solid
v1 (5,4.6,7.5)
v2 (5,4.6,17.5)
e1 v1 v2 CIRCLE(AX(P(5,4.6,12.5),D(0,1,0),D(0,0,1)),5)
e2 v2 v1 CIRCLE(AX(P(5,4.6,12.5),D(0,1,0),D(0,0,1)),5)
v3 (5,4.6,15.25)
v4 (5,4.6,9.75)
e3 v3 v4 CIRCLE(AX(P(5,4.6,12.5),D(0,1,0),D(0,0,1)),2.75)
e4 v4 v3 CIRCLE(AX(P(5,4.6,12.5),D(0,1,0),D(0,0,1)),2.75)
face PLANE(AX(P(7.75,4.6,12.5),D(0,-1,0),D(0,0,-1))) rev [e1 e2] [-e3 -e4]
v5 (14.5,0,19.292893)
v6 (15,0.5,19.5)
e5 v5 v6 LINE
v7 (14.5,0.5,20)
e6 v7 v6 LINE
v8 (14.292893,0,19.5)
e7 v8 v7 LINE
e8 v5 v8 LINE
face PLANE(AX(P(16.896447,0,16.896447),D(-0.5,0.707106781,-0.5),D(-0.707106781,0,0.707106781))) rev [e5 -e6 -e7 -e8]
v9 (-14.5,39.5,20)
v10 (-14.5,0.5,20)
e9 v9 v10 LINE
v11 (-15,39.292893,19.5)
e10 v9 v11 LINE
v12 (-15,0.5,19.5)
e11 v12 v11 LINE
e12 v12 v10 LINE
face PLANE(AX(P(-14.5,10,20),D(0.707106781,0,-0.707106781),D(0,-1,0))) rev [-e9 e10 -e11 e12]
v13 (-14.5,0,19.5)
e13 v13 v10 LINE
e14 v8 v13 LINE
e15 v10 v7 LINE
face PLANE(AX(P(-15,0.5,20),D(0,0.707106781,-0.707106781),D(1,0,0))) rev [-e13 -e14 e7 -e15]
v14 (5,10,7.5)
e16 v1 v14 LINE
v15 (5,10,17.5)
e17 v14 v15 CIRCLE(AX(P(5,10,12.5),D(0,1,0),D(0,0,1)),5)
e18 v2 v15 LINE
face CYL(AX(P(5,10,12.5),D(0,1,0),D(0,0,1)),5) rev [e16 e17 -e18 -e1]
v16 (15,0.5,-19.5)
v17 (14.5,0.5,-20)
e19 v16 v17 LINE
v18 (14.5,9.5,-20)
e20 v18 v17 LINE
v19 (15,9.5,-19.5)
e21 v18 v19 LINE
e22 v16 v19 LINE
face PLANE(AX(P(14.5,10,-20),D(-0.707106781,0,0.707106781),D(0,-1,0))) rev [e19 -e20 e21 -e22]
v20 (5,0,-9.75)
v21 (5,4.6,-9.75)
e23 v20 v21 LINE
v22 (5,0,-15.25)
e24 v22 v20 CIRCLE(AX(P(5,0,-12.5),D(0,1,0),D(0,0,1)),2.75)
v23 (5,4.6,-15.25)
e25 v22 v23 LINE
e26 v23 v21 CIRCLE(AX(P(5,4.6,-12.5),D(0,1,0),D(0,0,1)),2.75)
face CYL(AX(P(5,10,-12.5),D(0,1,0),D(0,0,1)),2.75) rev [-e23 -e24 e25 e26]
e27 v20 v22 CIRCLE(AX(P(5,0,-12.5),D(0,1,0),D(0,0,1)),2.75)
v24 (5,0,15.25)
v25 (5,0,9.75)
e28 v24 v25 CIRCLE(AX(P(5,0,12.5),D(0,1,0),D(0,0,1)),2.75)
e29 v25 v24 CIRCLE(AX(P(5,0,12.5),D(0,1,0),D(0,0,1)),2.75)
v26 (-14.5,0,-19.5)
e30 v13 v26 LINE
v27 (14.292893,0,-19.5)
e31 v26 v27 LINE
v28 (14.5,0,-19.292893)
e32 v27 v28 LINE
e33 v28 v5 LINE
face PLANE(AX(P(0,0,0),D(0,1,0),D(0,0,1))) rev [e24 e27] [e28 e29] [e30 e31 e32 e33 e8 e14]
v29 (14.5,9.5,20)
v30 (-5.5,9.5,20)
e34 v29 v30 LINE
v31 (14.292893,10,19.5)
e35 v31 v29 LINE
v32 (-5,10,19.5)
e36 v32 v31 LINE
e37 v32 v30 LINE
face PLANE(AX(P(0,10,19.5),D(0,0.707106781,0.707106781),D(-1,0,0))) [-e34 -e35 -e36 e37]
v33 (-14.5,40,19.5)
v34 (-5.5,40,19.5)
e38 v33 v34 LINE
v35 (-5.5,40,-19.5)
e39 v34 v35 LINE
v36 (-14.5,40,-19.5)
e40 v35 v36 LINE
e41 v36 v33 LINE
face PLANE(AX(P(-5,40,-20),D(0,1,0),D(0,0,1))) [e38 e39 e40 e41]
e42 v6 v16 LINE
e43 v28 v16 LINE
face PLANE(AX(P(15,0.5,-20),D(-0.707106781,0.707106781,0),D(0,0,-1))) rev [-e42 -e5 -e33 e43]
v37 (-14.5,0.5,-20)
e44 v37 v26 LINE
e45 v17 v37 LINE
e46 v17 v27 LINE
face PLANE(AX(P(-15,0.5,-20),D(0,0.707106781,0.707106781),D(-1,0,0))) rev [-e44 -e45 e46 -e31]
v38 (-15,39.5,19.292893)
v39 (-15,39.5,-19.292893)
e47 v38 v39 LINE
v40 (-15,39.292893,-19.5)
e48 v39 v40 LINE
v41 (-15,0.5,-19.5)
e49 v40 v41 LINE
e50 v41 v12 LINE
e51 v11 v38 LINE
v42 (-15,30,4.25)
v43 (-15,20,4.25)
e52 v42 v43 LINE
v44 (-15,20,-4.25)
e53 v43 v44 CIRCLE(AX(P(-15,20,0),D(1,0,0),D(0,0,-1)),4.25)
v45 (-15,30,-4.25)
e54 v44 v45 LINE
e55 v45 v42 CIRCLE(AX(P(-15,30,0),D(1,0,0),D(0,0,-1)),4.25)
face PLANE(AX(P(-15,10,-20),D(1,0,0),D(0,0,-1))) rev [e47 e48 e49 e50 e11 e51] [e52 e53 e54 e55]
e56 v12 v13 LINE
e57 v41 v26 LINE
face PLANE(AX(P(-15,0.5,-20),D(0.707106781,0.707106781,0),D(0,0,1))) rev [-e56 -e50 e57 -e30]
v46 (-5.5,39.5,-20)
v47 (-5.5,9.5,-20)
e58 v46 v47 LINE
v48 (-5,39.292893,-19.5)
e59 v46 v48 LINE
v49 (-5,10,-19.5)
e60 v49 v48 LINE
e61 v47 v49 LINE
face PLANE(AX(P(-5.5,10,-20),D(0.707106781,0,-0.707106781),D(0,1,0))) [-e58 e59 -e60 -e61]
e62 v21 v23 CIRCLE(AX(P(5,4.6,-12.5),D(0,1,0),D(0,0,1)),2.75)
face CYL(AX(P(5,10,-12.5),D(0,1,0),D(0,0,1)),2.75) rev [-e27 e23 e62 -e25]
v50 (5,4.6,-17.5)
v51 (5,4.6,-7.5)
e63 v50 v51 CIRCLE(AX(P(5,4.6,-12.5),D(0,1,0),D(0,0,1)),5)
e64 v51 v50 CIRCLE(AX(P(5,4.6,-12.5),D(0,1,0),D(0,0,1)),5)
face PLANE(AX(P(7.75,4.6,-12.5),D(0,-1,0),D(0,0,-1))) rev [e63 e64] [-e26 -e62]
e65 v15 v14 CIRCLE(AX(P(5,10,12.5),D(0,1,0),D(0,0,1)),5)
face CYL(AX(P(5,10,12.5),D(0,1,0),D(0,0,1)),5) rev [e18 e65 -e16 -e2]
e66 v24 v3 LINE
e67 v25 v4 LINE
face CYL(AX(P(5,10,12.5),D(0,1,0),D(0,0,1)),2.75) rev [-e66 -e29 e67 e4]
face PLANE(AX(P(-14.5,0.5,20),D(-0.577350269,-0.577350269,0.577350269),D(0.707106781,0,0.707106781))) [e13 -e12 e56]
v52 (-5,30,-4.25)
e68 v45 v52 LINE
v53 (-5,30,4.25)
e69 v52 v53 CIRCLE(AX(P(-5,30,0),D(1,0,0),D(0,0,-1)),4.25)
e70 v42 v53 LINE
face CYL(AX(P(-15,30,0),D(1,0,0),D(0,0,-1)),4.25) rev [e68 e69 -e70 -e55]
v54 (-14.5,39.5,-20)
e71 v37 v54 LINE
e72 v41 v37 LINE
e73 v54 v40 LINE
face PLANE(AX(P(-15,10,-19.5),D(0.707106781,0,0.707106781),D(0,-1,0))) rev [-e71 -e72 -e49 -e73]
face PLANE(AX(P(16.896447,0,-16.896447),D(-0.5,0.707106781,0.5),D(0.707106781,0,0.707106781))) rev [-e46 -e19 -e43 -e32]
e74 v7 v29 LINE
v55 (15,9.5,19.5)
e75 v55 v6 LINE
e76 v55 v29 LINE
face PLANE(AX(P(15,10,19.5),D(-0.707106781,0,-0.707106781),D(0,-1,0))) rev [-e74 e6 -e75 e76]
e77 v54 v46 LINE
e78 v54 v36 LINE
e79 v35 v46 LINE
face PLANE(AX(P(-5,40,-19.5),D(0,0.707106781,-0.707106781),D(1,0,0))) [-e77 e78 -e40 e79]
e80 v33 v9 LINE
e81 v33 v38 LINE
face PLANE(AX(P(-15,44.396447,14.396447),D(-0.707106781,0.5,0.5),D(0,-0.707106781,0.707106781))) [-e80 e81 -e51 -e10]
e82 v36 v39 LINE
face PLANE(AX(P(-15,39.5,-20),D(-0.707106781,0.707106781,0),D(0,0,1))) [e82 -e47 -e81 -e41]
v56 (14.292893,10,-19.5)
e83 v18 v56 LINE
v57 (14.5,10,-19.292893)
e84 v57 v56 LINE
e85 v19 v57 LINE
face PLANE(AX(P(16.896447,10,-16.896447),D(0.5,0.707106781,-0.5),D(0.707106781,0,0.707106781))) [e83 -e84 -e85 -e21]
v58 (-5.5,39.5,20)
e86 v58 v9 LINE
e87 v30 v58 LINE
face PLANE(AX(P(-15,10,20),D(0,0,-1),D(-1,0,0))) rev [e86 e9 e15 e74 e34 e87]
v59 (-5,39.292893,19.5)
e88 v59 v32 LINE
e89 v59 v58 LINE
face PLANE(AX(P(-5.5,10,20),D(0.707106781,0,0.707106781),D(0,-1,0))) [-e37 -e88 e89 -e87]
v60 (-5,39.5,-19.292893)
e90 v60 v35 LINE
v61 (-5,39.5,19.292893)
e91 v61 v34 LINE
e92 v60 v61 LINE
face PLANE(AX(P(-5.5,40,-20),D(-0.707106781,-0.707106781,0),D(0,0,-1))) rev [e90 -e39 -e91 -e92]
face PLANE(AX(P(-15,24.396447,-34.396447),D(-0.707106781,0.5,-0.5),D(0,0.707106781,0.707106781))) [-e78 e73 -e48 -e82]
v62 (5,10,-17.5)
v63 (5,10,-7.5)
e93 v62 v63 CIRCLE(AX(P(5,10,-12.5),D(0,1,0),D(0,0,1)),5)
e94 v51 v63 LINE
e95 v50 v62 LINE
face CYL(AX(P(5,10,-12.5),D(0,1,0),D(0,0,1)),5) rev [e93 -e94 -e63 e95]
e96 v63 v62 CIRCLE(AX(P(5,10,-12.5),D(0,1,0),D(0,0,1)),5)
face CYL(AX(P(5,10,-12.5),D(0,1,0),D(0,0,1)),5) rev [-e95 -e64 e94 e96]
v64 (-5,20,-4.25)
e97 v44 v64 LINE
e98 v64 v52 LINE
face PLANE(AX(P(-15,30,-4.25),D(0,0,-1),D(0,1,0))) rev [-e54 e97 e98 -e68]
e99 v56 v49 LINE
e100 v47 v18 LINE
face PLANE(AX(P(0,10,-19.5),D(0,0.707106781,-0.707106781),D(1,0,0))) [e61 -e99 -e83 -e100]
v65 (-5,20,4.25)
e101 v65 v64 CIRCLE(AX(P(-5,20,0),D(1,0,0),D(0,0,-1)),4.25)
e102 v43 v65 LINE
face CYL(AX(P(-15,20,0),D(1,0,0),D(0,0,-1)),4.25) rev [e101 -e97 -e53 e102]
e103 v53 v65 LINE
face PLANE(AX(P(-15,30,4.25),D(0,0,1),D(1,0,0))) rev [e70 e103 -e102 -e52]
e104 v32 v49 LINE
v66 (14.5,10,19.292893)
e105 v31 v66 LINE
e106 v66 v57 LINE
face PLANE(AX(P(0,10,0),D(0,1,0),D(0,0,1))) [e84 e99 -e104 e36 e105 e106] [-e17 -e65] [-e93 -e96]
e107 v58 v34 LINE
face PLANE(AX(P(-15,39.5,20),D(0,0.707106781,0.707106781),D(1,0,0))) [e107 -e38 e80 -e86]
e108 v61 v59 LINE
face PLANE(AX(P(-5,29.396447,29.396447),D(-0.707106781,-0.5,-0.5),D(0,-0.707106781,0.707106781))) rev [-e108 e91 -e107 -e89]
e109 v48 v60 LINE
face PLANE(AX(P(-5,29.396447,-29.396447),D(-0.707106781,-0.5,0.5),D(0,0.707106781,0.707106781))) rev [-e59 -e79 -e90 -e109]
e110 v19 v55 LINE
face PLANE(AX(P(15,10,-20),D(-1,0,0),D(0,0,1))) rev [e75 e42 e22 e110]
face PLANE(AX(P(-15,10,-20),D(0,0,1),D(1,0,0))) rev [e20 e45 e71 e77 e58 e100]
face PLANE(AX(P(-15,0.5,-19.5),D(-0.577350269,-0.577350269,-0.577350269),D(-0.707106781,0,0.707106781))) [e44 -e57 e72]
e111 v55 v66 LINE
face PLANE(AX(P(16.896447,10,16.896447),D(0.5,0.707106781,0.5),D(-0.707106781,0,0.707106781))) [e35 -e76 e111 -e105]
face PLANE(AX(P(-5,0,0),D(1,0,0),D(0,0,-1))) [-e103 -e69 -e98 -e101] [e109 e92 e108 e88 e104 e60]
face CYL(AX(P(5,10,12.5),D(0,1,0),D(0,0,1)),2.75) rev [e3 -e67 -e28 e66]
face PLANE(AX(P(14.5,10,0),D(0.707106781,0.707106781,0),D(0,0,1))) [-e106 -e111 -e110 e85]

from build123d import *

# Parameters (mm, degrees)
SKETCH_1_W                   = 30
SKETCH_1_H                   = 40
EXTRUDE_1_DEPTH              = 10
SKETCH_2_W                   = 40
SKETCH_2_H                   = 40
EXTRUDE_2_DEPTH              = 10
HOLE_WIZARD_M5_1_D           = 5.5
HOLE_WIZARD_M5_1_CBORE_D     = 10
HOLE_WIZARD_M5_1_CBORE_DEPTH = 5.4
CHAMFER_1_SIZE               = 0.5
CUT_EXTRUDE_1_DEPTH          = 49.989794856
CHAMFER_2_SIZE               = 0.5
CHAMFER_3_SIZE               = 0.5


with BuildPart() as part:
    # 草图1 → 凸台-拉伸1 (new body)
    with BuildSketch(Plane(origin=(0, 0, 0), x_dir=(1, 0, 0), z_dir=(0, 1, 0))):
        Rectangle(SKETCH_1_W, SKETCH_1_H)
    extrude(amount=EXTRUDE_1_DEPTH)

    # 草图2 → 凸台-拉伸2 (add)
    with BuildSketch(Plane.ZY.offset(15)):
        with Locations((0, 20)):
            Rectangle(SKETCH_2_W, SKETCH_2_H)
    extrude(amount=-EXTRUDE_2_DEPTH)

    # M5 六角凹头螺钉的柱形沉头孔1 (through all)
    with Locations(Plane(origin=(0, 10, 0), x_dir=(1, 0, 0), z_dir=(0, 1, 0))):
        with Locations((5, -12.5), (5, 12.5)):
            CounterBoreHole(HOLE_WIZARD_M5_1_D / 2, HOLE_WIZARD_M5_1_CBORE_D / 2, HOLE_WIZARD_M5_1_CBORE_DEPTH)

    # 倒角1
    chamfer_1_edges = [part.edges().sort_by_distance(p)[0] for p in [
        (15, 5, 20),
        (15, 5, -20),
    ]]
    chamfer(chamfer_1_edges, length=CHAMFER_1_SIZE)

    # 草图5 → 切除-拉伸1 (cut, through all)
    with BuildSketch(Plane(origin=(-5, 0, 0), x_dir=(0, 0, -1), z_dir=(1, 0, 0))):
        with BuildLine():
            Line((4.25, 30), (4.25, 20))
            ThreePointArc((4.25, 20), (0, 15.75), (-4.25, 20))
            Line((-4.25, 20), (-4.25, 30))
            ThreePointArc((-4.25, 30), (0, 34.25), (4.25, 30))
        make_face()
    extrude(amount=-CUT_EXTRUDE_1_DEPTH, mode=Mode.SUBTRACT)

    # 倒角2
    chamfer_2_edges = [part.edges().sort_by_distance(p)[0] for p in [
        (-10, 40, -20),
        (-10, 40, 20),
    ]]
    chamfer(chamfer_2_edges, length=CHAMFER_2_SIZE)

    # 倒角3
    chamfer_3_edges = [part.edges().sort_by_distance(p)[0] for p in [
        (4.75, 10, 20),
        (-5, 24.75, 20),
        (-0.25, 0, 20),
        (-15, 0, 0),
        (-0.25, 0, -20),
        (4.75, 10, -20),
        (15, 0, 0),
        (14.75, 0, 19.75),
        (14.75, 0, -19.75),
        (15, 10, 0),
        (14.75, 10, 19.75),
        (14.75, 10, -19.75),
        (-15, 19.75, 20),
        (-15, 40, 0),
        (-15, 19.75, -20),
        (-15, 39.75, -19.75),
        (-15, 39.75, 19.75),
        (-5, 40, 0),
        (-5, 24.75, -20),
        (-5, 39.75, -19.75),
        (-5, 39.75, 19.75),
    ]]
    chamfer(chamfer_3_edges, length=CHAMFER_3_SIZE)


solid = part.part
